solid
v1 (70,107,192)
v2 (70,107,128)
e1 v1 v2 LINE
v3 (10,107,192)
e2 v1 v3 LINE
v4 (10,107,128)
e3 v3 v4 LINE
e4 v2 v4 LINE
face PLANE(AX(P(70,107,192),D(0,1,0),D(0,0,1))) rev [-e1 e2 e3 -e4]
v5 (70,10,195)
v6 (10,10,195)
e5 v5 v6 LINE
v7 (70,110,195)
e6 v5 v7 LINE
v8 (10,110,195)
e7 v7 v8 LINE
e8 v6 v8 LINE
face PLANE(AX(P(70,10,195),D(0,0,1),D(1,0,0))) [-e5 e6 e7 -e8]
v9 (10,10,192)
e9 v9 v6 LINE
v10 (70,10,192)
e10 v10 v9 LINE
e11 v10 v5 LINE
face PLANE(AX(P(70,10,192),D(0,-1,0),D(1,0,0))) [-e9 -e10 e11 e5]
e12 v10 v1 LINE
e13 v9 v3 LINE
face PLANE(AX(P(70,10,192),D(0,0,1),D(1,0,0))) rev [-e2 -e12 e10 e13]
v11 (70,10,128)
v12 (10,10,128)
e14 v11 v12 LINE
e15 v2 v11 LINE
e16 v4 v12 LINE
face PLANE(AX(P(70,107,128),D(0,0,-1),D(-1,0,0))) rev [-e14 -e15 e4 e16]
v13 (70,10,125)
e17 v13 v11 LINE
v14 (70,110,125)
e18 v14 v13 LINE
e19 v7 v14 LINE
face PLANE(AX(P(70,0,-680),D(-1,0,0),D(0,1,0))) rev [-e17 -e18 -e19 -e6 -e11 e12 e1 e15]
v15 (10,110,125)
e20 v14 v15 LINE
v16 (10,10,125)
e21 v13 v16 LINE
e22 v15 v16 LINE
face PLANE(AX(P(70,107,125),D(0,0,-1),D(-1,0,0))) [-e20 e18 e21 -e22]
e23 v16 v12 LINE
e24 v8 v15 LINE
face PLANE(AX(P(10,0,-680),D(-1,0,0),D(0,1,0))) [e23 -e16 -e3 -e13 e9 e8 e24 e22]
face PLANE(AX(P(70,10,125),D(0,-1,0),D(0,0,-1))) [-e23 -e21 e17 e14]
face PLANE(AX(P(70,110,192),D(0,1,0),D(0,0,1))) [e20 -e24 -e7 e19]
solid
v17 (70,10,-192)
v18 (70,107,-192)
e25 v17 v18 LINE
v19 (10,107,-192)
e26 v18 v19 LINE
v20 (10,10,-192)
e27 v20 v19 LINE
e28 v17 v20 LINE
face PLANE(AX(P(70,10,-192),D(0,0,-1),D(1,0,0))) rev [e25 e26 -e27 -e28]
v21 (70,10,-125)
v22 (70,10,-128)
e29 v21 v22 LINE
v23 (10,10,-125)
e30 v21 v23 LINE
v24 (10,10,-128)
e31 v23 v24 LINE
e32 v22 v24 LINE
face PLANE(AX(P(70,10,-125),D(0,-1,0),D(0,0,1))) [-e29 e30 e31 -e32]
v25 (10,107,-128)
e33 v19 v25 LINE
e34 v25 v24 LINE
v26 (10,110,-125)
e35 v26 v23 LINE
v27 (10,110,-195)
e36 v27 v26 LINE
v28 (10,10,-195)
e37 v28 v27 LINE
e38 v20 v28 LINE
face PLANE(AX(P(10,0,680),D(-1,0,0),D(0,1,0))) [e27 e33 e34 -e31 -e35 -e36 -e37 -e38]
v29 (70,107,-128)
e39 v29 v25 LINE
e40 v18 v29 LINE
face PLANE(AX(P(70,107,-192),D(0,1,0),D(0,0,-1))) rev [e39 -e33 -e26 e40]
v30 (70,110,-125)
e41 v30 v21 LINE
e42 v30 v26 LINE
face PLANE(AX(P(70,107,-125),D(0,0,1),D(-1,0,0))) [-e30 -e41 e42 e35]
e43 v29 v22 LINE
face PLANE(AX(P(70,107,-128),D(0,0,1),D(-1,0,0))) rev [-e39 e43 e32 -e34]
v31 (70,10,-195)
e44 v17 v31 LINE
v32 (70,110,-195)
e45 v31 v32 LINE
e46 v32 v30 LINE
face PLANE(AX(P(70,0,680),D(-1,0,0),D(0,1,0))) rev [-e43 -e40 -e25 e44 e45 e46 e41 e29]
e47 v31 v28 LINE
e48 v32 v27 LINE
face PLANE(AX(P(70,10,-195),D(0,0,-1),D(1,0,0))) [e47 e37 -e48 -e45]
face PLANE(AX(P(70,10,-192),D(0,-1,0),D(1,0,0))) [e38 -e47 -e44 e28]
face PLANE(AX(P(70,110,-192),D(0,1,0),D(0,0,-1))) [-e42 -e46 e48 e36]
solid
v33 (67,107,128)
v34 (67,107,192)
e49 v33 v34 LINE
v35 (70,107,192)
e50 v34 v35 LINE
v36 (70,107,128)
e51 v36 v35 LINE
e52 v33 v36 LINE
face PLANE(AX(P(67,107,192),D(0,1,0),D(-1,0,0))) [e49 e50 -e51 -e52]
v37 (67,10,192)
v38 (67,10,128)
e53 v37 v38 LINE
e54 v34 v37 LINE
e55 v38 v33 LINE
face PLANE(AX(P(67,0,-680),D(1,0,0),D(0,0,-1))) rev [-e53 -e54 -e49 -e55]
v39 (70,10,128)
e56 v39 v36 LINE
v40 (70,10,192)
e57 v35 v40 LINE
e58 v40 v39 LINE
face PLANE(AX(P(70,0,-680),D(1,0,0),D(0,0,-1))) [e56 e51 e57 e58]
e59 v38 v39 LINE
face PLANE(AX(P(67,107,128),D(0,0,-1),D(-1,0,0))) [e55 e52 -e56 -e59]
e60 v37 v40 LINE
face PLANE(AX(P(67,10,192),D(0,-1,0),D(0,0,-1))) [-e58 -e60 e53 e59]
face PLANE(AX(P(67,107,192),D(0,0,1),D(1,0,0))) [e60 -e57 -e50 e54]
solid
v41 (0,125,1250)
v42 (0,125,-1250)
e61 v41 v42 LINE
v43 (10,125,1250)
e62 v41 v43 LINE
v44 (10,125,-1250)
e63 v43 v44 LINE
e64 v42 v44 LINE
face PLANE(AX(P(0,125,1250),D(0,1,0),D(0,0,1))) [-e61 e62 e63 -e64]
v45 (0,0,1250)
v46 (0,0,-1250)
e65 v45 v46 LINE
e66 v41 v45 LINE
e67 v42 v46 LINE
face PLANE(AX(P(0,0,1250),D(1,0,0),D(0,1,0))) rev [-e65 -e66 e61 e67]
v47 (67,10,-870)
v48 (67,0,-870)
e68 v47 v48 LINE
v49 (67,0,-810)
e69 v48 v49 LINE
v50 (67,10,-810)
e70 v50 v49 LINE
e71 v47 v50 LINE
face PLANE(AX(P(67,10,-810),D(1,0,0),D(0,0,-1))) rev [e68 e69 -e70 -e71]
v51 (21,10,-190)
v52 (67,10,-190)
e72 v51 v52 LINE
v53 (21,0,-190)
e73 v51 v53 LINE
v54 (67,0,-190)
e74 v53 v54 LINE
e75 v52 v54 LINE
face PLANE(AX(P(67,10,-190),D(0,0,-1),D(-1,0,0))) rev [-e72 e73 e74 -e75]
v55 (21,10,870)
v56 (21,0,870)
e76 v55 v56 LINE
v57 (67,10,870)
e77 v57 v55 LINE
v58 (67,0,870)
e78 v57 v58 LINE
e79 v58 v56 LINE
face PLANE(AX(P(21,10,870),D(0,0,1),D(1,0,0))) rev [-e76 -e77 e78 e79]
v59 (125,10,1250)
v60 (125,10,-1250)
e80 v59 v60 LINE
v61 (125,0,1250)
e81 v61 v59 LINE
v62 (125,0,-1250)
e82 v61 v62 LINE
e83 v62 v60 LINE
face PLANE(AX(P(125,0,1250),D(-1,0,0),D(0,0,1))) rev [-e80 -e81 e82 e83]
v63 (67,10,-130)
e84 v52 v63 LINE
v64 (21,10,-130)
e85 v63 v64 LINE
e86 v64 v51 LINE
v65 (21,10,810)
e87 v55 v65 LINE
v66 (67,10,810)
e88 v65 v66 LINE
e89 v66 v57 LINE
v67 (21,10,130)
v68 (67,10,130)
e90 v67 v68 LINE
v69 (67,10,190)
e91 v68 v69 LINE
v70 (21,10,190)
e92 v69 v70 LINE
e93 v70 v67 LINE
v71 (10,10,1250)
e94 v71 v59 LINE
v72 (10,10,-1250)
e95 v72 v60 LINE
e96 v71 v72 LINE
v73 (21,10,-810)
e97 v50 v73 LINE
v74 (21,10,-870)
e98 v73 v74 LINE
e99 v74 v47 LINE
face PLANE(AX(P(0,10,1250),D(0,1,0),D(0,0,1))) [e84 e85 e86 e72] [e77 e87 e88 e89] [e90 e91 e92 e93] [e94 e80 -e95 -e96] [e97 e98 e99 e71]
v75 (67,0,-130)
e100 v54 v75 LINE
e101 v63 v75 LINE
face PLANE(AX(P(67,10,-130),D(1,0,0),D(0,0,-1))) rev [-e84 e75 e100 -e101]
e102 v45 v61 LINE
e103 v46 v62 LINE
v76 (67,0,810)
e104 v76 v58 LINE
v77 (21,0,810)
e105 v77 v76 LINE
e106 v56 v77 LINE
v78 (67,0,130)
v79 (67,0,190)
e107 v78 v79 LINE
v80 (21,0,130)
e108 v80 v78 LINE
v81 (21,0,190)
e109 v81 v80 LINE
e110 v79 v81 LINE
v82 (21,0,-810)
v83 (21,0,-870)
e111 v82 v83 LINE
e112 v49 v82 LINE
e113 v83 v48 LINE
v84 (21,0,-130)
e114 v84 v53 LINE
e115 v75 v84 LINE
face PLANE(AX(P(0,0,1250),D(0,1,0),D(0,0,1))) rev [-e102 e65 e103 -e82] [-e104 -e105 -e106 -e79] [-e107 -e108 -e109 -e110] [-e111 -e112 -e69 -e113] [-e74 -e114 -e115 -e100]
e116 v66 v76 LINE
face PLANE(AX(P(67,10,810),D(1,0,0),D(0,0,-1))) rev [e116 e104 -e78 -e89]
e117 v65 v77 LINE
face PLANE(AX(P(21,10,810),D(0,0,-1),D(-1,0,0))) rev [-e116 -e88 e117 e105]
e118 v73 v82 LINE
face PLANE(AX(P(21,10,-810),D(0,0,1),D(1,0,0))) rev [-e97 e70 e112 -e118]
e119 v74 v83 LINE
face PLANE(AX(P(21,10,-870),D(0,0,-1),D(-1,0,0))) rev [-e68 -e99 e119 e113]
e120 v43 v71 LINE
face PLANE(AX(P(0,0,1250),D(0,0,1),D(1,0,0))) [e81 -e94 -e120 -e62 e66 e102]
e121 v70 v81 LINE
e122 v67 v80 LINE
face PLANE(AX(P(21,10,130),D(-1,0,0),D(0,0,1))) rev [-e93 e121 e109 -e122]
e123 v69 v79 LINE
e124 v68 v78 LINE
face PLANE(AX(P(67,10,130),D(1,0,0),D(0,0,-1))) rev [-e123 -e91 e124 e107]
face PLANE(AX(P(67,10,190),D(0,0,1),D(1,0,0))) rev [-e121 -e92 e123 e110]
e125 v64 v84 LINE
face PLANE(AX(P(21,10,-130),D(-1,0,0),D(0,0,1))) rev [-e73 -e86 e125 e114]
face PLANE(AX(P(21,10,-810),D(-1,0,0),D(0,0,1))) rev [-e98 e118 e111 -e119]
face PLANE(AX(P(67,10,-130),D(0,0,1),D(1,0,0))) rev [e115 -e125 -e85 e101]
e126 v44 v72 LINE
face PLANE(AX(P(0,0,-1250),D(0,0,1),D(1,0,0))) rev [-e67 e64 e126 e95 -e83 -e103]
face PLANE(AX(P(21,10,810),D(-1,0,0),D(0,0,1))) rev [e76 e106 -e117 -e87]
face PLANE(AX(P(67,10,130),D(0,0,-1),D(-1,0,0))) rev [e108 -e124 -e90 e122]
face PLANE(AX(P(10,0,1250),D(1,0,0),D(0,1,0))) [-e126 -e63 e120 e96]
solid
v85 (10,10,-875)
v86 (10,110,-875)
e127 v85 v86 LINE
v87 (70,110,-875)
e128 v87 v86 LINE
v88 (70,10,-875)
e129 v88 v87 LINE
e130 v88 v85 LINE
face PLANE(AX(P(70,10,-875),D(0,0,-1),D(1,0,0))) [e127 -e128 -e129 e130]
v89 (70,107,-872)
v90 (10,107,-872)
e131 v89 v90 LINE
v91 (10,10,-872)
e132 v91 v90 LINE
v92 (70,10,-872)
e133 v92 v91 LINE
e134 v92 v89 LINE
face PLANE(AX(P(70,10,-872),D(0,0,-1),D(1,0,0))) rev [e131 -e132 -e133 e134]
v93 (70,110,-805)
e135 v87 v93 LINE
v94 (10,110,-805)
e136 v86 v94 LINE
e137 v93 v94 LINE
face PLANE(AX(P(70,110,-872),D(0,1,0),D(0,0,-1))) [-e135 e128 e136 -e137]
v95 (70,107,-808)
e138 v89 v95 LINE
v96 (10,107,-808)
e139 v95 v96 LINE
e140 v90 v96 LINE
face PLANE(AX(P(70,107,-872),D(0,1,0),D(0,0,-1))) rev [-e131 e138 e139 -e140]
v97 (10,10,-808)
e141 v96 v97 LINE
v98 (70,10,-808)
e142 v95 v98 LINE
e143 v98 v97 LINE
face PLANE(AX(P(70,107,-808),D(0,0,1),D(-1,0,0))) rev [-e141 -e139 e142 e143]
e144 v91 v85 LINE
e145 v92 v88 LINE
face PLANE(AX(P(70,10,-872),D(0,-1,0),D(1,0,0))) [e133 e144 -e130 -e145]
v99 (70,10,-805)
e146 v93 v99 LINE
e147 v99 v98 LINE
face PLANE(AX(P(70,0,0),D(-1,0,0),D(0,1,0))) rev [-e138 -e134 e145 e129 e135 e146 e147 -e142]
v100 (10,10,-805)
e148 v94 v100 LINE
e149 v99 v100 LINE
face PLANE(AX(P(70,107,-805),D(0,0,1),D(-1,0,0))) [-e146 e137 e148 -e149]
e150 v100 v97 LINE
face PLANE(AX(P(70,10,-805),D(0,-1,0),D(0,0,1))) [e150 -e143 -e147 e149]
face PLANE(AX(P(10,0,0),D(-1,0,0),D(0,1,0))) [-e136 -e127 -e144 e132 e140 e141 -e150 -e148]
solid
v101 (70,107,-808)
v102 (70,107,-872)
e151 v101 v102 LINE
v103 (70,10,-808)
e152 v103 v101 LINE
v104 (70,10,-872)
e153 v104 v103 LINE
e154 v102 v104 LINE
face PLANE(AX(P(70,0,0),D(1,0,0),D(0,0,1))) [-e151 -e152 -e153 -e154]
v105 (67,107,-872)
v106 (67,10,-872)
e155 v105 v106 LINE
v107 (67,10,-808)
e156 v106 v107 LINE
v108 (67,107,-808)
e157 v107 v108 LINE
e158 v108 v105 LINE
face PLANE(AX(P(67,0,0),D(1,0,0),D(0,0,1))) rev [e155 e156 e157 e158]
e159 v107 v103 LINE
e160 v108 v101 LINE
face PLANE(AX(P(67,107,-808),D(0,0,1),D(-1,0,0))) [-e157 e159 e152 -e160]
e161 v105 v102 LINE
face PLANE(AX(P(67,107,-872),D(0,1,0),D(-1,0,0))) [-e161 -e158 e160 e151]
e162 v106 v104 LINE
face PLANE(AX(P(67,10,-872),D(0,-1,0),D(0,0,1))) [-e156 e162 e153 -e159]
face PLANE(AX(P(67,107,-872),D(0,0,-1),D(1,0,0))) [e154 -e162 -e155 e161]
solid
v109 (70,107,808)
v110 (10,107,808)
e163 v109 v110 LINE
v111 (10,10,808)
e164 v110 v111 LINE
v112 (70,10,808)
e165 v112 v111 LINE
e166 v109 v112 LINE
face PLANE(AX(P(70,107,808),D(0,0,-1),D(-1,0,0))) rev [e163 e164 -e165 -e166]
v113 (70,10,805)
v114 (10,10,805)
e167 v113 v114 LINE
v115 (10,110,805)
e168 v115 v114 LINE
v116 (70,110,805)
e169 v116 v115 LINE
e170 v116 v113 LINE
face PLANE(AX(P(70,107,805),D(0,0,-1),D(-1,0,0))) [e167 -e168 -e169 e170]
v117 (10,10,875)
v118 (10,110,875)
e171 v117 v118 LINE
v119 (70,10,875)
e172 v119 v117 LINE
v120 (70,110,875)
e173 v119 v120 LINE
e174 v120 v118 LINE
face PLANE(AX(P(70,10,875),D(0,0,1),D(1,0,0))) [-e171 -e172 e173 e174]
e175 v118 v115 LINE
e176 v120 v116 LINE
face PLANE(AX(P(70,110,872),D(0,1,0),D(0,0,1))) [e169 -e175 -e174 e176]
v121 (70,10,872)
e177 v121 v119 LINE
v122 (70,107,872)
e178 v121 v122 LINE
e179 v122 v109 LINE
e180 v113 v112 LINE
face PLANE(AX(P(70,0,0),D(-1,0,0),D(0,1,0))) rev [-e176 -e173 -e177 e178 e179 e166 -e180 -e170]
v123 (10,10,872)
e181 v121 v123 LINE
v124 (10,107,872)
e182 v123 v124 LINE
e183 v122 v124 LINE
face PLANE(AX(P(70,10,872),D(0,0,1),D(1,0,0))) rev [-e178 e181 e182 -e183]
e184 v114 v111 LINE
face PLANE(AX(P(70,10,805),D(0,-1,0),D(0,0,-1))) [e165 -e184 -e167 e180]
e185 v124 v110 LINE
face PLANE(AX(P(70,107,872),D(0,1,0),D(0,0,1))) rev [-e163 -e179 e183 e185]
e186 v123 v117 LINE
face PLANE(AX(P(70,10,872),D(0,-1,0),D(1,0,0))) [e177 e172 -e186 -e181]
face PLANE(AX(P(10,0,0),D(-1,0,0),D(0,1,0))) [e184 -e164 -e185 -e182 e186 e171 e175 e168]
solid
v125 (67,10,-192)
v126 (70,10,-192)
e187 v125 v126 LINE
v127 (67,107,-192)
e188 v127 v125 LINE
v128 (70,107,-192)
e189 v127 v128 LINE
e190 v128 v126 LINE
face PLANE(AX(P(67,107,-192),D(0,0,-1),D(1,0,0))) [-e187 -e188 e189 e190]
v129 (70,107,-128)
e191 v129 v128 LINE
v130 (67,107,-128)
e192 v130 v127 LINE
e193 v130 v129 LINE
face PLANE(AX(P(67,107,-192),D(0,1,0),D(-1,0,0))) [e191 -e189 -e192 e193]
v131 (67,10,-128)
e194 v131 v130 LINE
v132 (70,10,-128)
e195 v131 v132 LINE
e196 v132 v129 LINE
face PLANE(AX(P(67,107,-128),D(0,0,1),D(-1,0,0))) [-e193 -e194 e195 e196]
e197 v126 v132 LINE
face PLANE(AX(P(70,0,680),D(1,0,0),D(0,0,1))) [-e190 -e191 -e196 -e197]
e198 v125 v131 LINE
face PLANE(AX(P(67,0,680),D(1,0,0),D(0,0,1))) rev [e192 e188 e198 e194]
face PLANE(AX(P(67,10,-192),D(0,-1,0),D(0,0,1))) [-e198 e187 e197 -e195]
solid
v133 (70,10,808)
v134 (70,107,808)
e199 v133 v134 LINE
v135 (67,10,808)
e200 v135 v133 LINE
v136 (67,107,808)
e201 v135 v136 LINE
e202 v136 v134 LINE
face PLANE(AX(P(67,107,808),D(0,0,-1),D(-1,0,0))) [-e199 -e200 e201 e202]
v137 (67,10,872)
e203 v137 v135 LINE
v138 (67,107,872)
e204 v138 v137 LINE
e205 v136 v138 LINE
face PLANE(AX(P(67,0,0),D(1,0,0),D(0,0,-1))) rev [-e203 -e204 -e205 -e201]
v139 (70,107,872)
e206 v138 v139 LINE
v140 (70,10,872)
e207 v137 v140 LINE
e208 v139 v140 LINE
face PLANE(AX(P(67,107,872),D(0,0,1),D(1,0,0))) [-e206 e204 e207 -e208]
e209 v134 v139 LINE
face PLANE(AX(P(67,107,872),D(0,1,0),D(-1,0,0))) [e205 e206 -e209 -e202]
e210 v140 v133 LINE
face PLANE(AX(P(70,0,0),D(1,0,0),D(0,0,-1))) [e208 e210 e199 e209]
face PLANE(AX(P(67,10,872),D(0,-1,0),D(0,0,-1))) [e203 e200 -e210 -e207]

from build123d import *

# Parameters (mm, degrees)
EXTRUDE_1_DEPTH        = 1250
EXTRUDE_1_2_DEPTH      = 60
SKETCH_3_W             = 64
SKETCH_3_H             = 97
EXTRUDE_2_DEPTH        = 3
PATTERN_LINEAR_1_COUNT = 2
PATTERN_LINEAR_1_PITCH = 680
SKETCH_4_W             = 46
SKETCH_4_H             = 60
CUT_EXTRUDE_1_DEPTH    = 10


with BuildPart() as part:
    # 草图1 → Extrude 1 (new, symmetric)
    with BuildSketch(Plane.XY):
        Polygon((0, 125), (10, 125), (10, 10), (125, 10), (125, 0), (0, 0), align=None)
    extrude(amount=EXTRUDE_1_DEPTH, both=True)

    # 草图4 → 切除-拉伸1 (cut)
    with BuildSketch(Plane.XZ):
        with Locations((44, 160)):
            Rectangle(SKETCH_4_W, SKETCH_4_H)
        with Locations((44, 840)):
            Rectangle(SKETCH_4_W, SKETCH_4_H)
        with Locations((44, -840)):
            Rectangle(SKETCH_4_W, SKETCH_4_H)
        with Locations((44, -160)):
            Rectangle(SKETCH_4_W, SKETCH_4_H)
    extrude(amount=-CUT_EXTRUDE_1_DEPTH, mode=Mode.SUBTRACT)


with BuildPart() as body_2:
    # 草图2 → Extrude 1 2 (new body)
    with BuildSketch(Plane(origin=(10, 0, 0), x_dir=(0, 0, -1), z_dir=(1, 0, 0))):
        Polygon((-872, 10), (-872, 107), (-808, 107), (-808, 10), (-805, 10), (-805, 110), (-875, 110), (-875, 10), align=None)
    extrude(amount=EXTRUDE_1_2_DEPTH)


with BuildPart() as body_3:
    # 草图3 → 凸台-拉伸2 (new body)
    with BuildSketch(Plane(origin=(70, 0, 0), x_dir=(0, 0, -1), z_dir=(1, 0, 0))):
        with Locations((-840, 58.5)):
            Rectangle(SKETCH_3_W, SKETCH_3_H)
    extrude(amount=-EXTRUDE_2_DEPTH)


with BuildPart() as pattern_linear_1_1:
    # 阵列(线性)1: pattern copy
    add(body_2.part.moved(Location(Vector(0, 0, -1) * (1 * PATTERN_LINEAR_1_PITCH))))


with BuildPart() as pattern_linear_1_2:
    # 阵列(线性)1: pattern copy
    add(body_3.part.moved(Location(Vector(0, 0, -1) * (1 * PATTERN_LINEAR_1_PITCH))))


with BuildPart() as body_6:
    # 镜向1: mirrored copy
    add(pattern_linear_1_2.part.mirror(Plane.XY))


with BuildPart() as body_7:
    # Mirror 1 2: mirrored copy
    add(body_2.part.mirror(Plane.XY))


with BuildPart() as body_8:
    # Mirror 1 3: mirrored copy
    add(pattern_linear_1_1.part.mirror(Plane.XY))


with BuildPart() as body_9:
    # Mirror 1 4: mirrored copy
    add(body_3.part.mirror(Plane.XY))


solid = Compound([part.part, body_2.part, body_3.part, pattern_linear_1_1.part, pattern_linear_1_2.part, body_6.part, body_7.part, body_8.part, body_9.part])
